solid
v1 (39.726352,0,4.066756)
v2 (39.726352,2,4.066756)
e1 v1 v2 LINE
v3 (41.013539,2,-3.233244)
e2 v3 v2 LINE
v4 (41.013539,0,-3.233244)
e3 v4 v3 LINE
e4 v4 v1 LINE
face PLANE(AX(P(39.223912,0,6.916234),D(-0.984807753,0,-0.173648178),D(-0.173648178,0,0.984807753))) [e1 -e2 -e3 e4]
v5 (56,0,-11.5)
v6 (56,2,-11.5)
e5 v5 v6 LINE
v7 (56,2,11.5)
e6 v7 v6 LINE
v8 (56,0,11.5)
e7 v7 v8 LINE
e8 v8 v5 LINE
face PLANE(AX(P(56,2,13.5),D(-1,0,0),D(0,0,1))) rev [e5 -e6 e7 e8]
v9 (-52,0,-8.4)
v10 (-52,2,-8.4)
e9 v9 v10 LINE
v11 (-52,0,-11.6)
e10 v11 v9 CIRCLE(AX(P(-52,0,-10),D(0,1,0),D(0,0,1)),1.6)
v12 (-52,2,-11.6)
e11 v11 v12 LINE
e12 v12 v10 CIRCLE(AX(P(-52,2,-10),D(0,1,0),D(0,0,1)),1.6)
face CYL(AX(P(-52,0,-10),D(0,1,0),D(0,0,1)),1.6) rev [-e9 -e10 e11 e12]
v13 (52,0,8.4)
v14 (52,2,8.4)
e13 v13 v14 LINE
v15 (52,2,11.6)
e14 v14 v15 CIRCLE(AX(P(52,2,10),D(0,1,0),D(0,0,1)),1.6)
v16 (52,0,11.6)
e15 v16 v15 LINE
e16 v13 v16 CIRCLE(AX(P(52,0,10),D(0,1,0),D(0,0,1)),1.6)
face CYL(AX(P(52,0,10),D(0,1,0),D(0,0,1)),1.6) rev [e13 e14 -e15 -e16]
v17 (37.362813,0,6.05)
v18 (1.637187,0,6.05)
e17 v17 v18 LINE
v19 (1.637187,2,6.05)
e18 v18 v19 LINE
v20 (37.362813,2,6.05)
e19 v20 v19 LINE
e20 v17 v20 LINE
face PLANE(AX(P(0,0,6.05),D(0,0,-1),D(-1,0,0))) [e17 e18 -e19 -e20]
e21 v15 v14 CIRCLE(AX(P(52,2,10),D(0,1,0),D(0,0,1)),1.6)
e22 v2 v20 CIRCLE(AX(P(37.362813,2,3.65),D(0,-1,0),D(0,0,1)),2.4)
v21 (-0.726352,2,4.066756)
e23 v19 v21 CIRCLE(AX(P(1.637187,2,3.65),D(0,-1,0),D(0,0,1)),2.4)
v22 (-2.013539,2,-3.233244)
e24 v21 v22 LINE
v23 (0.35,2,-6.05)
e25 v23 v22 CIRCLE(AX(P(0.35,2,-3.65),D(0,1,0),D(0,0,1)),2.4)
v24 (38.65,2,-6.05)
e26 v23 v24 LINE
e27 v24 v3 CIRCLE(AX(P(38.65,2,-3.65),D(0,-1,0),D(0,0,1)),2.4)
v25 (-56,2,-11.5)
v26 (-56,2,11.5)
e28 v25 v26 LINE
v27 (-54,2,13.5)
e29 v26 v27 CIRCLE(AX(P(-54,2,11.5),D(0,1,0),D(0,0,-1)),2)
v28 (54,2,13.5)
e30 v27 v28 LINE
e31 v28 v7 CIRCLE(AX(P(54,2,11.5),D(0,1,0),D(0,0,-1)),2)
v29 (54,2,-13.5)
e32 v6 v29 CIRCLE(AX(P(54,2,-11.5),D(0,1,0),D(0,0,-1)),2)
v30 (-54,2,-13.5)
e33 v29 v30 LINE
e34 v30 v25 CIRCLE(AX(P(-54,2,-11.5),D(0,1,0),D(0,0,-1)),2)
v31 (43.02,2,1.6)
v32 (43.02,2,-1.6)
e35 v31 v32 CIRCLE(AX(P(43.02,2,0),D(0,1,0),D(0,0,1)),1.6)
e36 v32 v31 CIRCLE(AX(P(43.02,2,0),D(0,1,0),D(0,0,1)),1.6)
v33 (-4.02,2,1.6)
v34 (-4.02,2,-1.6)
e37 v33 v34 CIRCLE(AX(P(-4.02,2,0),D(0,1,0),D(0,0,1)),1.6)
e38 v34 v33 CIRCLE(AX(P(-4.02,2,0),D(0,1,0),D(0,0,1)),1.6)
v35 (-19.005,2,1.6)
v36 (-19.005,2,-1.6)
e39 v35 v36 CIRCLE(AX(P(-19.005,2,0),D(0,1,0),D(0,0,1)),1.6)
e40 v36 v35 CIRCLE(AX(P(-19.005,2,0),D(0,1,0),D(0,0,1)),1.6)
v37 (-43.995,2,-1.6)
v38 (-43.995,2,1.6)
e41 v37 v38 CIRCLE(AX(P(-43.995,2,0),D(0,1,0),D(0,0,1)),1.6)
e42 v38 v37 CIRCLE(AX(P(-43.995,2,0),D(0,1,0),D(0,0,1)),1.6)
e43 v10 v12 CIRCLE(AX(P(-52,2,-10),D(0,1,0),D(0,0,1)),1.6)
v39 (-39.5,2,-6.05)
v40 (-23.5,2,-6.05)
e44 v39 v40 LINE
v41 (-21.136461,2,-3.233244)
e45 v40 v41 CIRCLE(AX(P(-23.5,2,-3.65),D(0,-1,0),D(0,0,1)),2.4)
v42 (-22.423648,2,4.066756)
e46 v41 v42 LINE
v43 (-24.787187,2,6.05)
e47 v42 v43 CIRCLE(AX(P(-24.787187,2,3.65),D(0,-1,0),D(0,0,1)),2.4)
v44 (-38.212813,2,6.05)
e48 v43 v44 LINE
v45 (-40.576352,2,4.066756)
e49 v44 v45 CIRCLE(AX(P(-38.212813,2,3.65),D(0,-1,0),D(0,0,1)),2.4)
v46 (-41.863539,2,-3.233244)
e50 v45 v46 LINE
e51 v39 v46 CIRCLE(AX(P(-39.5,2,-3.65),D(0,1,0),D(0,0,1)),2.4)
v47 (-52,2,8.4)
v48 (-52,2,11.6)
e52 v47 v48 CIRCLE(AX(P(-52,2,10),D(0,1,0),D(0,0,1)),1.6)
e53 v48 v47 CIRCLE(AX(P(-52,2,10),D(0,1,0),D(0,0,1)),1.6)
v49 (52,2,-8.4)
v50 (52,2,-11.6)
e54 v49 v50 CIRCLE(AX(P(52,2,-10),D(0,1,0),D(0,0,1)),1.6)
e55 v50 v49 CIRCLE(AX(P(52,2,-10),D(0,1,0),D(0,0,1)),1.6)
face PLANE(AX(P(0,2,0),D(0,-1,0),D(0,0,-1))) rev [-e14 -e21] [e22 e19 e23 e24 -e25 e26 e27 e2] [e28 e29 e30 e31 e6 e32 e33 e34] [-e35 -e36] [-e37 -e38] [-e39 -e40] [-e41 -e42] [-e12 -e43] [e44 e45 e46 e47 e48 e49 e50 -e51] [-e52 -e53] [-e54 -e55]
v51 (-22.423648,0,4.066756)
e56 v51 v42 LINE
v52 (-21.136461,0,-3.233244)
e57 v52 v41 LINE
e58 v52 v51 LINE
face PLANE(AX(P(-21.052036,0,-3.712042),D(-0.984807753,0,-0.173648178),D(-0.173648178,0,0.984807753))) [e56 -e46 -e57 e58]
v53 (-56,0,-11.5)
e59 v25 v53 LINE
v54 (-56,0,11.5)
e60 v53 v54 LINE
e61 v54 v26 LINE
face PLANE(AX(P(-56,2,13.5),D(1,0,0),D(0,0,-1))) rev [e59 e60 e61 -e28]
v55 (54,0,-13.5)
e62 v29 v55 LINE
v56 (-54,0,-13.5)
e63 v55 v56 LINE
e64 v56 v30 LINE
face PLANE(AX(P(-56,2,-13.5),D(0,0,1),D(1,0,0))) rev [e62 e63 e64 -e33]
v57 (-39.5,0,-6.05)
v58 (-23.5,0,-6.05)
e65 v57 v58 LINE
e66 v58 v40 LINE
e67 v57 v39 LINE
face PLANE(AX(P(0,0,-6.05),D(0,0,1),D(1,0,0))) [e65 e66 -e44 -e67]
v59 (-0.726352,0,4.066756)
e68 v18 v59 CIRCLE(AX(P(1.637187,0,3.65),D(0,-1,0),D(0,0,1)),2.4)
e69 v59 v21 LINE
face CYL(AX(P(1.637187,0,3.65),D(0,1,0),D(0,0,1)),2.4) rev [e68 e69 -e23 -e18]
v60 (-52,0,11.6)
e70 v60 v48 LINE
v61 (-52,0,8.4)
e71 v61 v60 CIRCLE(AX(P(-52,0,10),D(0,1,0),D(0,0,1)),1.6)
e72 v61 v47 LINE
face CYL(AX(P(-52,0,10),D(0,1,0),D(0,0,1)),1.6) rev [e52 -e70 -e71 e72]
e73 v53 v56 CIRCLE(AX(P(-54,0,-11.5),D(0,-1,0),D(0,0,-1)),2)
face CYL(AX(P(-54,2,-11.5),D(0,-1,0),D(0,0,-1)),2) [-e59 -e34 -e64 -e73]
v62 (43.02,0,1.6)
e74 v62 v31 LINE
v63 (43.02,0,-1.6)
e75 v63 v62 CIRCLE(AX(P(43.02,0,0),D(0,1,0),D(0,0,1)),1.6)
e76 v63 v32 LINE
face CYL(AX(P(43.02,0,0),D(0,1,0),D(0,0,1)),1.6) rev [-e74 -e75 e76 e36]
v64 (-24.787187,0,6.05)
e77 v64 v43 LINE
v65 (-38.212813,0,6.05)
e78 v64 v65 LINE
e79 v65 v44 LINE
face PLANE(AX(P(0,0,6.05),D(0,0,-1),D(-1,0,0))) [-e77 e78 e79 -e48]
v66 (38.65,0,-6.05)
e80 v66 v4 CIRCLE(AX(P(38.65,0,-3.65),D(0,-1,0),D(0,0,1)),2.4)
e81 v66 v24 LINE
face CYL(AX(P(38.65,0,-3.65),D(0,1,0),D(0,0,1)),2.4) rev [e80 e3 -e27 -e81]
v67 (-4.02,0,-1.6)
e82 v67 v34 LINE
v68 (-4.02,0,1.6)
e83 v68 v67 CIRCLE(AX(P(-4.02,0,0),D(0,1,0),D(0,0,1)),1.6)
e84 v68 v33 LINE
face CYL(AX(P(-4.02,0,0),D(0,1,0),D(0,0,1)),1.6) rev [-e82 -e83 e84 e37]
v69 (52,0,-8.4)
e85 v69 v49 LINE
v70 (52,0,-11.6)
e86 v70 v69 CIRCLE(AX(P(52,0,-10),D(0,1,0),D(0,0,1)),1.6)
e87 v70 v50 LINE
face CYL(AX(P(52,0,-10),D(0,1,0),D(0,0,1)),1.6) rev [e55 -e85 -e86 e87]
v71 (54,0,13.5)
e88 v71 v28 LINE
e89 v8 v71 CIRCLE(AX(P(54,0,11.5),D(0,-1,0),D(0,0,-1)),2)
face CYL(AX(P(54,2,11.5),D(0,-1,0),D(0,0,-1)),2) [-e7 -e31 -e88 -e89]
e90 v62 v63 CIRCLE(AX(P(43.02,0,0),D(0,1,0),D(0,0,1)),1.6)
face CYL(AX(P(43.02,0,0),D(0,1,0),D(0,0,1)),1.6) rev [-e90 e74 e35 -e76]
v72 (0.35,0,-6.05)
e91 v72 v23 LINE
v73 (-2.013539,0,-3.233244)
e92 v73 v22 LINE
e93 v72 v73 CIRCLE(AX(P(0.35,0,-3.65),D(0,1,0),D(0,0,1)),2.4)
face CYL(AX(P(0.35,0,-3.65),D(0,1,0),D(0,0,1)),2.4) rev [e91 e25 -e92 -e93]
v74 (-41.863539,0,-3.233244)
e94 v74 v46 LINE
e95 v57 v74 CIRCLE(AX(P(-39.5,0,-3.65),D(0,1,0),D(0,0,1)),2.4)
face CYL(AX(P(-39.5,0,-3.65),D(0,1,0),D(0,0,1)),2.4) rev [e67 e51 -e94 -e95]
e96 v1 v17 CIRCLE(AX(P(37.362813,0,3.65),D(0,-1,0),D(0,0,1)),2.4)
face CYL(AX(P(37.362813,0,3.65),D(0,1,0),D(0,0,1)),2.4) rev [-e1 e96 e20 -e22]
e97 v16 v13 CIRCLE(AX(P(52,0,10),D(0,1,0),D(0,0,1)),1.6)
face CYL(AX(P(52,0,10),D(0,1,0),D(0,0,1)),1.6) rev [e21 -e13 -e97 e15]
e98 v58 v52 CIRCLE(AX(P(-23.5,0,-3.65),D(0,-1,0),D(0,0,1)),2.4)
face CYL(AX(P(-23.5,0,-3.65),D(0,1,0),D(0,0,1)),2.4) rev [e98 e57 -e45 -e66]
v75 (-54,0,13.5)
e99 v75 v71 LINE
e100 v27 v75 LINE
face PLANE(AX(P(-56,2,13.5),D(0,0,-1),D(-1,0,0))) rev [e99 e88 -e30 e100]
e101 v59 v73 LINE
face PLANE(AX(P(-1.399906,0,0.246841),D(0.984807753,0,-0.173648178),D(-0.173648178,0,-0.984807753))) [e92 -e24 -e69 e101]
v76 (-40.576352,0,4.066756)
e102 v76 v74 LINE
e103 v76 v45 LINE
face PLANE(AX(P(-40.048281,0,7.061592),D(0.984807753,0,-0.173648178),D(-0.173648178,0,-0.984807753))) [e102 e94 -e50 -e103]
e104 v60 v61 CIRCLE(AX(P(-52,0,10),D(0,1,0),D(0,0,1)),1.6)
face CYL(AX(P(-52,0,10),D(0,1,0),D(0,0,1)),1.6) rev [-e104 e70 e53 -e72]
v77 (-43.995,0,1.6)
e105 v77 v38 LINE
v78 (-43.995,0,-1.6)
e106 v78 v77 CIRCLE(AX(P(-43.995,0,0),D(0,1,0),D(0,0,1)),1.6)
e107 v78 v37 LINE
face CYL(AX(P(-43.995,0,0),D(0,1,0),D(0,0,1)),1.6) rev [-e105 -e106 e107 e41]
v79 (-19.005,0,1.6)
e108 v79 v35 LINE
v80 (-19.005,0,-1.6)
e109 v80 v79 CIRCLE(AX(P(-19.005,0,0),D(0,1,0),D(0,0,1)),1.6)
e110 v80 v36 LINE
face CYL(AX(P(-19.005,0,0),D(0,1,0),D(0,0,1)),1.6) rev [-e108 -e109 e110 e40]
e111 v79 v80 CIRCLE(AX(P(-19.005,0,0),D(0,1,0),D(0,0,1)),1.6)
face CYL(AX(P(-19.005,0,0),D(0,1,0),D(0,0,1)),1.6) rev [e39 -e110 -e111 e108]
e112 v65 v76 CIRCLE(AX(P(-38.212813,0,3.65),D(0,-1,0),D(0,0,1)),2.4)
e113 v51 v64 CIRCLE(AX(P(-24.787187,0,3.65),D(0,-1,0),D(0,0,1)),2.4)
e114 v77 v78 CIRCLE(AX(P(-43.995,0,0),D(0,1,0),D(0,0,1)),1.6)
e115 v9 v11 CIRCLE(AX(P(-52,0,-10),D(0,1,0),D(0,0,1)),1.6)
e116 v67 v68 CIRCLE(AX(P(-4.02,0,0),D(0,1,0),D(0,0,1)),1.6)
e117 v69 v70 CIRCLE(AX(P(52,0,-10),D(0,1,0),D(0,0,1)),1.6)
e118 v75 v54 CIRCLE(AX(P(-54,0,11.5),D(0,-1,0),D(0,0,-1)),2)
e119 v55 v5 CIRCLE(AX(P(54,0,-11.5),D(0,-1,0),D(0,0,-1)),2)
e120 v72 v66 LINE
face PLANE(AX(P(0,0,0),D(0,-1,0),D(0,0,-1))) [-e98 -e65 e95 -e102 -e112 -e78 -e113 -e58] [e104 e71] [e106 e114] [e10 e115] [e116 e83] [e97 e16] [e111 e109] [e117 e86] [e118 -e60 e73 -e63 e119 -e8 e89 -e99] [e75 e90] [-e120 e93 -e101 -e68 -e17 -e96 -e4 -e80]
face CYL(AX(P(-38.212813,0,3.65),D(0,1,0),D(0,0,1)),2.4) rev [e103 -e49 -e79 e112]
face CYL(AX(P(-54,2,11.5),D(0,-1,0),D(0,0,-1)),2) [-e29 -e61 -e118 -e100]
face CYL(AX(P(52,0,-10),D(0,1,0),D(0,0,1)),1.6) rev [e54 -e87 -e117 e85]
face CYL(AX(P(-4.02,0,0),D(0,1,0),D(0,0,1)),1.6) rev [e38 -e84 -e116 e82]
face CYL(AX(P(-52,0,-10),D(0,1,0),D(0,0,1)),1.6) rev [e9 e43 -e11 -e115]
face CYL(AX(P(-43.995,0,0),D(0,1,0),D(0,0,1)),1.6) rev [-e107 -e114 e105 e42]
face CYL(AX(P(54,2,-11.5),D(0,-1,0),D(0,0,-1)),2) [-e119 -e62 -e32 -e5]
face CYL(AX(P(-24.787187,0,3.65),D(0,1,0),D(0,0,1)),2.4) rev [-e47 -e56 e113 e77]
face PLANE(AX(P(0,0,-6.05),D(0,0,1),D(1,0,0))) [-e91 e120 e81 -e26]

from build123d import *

# Parameters (mm, degrees)
SKETCH1_W           = 112
SKETCH1_H           = 27
BOSS_EXTRUDE1_DEPTH = 2
SKETCH2_R           = 1.6
CUT_EXTRUDE1_DEPTH  = 58.638962517
FILLET1_R           = 2
SKETCH3_R           = 1.6
CUT_EXTRUDE2_DEPTH  = 2


with BuildPart() as part:
    # Sketch1 → Boss-Extrude1 (new body)
    with BuildSketch(Plane(origin=(0, 0, 0), x_dir=(1, 0, 0), z_dir=(0, 1, 0))):
        Rectangle(SKETCH1_W, SKETCH1_H)
    extrude(amount=BOSS_EXTRUDE1_DEPTH)

    # Sketch2 → Cut-Extrude1 (cut, through all)
    with BuildSketch(Plane(origin=(0, 2, 0), x_dir=(1, 0, 0), z_dir=(0, 1, 0))):
        with Locations(Location((-52, 10, 0), (0, 0, 270))):
            Circle(SKETCH2_R)
        with Locations(Location((52, 10, 0), (0, 0, 270))):
            Circle(SKETCH2_R)
        with Locations(Location((52, -10, 0), (0, 0, 270))):
            Circle(SKETCH2_R)
        with Locations(Location((-52, -10, 0), (0, 0, 270))):
            Circle(SKETCH2_R)
    extrude(amount=-CUT_EXTRUDE1_DEPTH, mode=Mode.SUBTRACT)

    # Fillet1
    fillet1_edges = [part.edges().sort_by_distance(p)[0] for p in [
        (56, 1, 13.5),
        (-56, 1, 13.5),
        (-56, 1, -13.5),
        (56, 1, -13.5),
    ]]
    fillet(fillet1_edges, radius=FILLET1_R)

    # Sketch3 → Cut-Extrude2 (cut)
    with BuildSketch(Plane(origin=(0, 2, 0), x_dir=(1, 0, 0), z_dir=(0, 1, 0))):
        with BuildLine():
            Line((1.637186959, -6.05), (37.362813041, -6.05))
            ThreePointArc((37.362813041, -6.05), (38.905503304, -5.488506663), (39.726351648, -4.066755626))
            Line((39.726351648, -4.066755626), (41.013538607, 3.233244374))
            ThreePointArc((41.013538607, 3.233244374), (40.488506663, 5.192690263), (38.65, 6.05))
            Line((38.65, 6.05), (0.35, 6.05))
            ThreePointArc((0.35, 6.05), (-1.488506663, 5.192690263), (-2.013538607, 3.233244374))
            Line((-2.013538607, 3.233244374), (-0.726351648, -4.066755626))
            ThreePointArc((-0.726351648, -4.066755626), (0.094496696, -5.488506663), (1.637186959, -6.05))
        make_face()
        with BuildLine():
            Line((-23.5, 6.05), (-39.5, 6.05))
            ThreePointArc((-39.5, 6.05), (-41.338506663, 5.192690263), (-41.863538607, 3.233244374))
            Line((-41.863538607, 3.233244374), (-40.576351648, -4.066755626))
            ThreePointArc((-40.576351648, -4.066755626), (-39.755503304, -5.488506663), (-38.212813041, -6.05))
            Line((-38.212813041, -6.05), (-24.787186959, -6.05))
            ThreePointArc((-24.787186959, -6.05), (-23.244496696, -5.488506663), (-22.423648352, -4.066755626))
            Line((-22.423648352, -4.066755626), (-21.136461393, 3.233244374))
            ThreePointArc((-21.136461393, 3.233244374), (-21.661493337, 5.192690263), (-23.5, 6.05))
        make_face()
        with Locations(Location((-43.995, 0, 0), (0, 0, 270))):
            Circle(SKETCH3_R)
        with Locations(Location((-19.005, 0, 0), (0, 0, 270))):
            Circle(SKETCH3_R)
        with Locations(Location((-4.02, 0, 0), (0, 0, 270))):
            Circle(SKETCH3_R)
        with Locations(Location((43.02, 0, 0), (0, 0, 270))):
            Circle(SKETCH3_R)
    extrude(amount=-CUT_EXTRUDE2_DEPTH, mode=Mode.SUBTRACT)


solid = part.part
